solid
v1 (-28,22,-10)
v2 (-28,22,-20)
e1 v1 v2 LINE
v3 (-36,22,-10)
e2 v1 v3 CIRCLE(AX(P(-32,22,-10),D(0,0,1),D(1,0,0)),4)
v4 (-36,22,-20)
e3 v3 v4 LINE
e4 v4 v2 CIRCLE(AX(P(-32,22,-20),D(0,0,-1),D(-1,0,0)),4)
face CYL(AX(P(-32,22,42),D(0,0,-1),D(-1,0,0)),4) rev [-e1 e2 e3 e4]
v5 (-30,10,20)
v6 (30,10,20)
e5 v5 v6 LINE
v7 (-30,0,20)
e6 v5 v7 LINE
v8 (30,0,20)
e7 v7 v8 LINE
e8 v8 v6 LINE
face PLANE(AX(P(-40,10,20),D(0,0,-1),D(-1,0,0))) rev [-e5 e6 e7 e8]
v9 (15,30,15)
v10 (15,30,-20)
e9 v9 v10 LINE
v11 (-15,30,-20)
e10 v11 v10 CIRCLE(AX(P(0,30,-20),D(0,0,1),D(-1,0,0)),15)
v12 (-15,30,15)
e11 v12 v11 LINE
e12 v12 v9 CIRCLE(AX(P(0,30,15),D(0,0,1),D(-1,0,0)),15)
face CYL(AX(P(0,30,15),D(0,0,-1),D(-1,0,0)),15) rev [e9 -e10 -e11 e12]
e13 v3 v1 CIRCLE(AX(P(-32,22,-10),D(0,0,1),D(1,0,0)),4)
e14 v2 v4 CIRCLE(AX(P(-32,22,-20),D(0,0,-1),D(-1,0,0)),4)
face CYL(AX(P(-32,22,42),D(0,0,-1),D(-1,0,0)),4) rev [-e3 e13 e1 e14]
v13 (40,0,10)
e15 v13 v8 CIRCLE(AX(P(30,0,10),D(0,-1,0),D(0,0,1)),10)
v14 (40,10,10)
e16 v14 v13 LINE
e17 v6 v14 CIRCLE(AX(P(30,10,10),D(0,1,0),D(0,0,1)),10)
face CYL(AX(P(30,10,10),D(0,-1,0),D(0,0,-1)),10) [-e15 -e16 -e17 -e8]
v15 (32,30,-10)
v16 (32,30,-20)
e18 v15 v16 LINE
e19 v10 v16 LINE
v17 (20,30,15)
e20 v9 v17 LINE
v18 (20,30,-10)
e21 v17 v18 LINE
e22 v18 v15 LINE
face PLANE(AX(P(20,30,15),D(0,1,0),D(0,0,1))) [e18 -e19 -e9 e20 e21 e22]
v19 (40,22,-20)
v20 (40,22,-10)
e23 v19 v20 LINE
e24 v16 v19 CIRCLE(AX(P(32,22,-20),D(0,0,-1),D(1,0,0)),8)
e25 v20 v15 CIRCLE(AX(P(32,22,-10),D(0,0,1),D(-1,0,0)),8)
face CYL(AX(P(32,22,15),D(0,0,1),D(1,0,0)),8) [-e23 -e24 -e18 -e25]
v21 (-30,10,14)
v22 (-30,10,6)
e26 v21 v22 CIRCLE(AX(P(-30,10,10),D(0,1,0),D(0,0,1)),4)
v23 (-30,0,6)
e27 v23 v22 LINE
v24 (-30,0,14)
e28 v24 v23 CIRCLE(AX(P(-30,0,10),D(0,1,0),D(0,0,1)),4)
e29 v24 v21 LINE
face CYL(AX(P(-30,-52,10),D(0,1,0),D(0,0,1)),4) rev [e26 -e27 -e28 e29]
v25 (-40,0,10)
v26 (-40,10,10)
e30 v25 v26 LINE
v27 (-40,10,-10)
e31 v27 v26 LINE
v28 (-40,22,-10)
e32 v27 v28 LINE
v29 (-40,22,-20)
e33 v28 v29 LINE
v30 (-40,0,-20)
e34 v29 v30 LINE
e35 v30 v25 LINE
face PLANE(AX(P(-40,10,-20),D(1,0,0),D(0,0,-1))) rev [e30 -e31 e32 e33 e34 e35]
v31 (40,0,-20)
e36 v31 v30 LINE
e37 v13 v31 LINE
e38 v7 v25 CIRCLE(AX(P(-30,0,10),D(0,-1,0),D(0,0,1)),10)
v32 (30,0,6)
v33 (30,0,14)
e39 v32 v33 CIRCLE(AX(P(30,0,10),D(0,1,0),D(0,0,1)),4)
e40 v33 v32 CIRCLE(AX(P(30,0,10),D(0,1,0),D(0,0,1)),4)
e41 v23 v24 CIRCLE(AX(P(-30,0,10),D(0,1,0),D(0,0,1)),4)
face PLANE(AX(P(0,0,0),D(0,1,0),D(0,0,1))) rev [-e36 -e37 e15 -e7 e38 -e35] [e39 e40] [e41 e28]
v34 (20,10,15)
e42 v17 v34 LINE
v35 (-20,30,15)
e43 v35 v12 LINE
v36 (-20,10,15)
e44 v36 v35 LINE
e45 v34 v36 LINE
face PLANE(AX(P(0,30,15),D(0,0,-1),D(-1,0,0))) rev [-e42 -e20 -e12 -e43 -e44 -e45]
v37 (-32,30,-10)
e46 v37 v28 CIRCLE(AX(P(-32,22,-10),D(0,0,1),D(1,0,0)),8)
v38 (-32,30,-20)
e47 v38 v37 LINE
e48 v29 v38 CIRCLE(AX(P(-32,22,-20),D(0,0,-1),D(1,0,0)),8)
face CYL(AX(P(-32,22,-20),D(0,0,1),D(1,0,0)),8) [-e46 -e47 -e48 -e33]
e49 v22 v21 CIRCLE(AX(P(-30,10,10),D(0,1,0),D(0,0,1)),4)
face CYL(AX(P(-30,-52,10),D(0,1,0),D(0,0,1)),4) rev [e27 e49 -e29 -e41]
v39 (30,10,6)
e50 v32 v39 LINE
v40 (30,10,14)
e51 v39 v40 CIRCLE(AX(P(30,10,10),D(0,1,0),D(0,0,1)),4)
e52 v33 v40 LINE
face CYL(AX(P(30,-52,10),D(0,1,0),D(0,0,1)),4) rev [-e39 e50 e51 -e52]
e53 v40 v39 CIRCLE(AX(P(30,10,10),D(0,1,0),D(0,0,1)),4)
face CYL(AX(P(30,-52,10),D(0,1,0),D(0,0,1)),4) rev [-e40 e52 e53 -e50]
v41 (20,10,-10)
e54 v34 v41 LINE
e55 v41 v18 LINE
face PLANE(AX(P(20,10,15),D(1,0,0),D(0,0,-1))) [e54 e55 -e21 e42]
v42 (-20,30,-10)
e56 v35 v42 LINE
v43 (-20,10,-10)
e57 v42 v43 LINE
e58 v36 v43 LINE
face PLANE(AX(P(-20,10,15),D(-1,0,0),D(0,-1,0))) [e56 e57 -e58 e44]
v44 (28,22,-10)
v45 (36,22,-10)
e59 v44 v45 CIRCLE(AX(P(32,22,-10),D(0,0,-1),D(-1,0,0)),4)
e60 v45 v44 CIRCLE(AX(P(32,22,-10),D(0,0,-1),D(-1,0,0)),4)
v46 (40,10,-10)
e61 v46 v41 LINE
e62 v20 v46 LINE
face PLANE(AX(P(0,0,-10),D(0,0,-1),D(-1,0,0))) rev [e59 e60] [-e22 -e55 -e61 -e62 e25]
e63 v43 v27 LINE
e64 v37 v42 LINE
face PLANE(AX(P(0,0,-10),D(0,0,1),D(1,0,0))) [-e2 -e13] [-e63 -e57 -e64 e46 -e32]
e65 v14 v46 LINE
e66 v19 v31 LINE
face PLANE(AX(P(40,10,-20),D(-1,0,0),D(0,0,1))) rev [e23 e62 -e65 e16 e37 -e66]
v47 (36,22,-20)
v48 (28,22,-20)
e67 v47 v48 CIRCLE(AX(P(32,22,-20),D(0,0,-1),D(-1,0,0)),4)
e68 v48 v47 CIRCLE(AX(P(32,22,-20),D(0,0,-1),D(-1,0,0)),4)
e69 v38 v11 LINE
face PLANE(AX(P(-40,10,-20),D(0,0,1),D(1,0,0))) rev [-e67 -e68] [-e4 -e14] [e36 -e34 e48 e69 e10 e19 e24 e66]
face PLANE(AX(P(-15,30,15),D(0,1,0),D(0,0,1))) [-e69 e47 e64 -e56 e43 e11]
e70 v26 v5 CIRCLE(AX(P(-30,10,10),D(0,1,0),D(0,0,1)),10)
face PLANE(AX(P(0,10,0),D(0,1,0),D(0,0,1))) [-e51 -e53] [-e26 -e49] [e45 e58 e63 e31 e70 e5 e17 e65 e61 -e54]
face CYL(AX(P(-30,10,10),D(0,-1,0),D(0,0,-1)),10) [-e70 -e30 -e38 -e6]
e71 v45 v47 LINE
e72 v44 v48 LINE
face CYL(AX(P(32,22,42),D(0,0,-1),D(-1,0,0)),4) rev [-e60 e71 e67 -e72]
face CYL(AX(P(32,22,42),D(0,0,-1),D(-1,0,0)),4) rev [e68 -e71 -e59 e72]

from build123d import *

# Parameters (mm, degrees)
BASE_PLATE_SKETCH_W       = 80
BASE_PLATE_SKETCH_H       = 40
BASE_PLATE_80X40X10_DEPTH = 10
BASE_CORNER_FILLETS_R10_R = 10
SADDLE_BLOCK_DEPTH        = 35
LUG_PROFILE_SKETCH_W      = 20
LUG_PROFILE_SKETCH_H      = 20
UPRIGHT_LUGS_DEPTH        = 10
LUG_TOP_FILLETS_R8_R      = 8
LUG_HOLE_SKETCH_R         = 4
LUG_HOLES_8_DEPTH         = 62
BASE_HOLE_SKETCH_R        = 4
BASE_HOLES_8_DEPTH        = 62


with BuildPart() as part:
    # Base Plate Sketch → Base Plate 80x40x10 (new body)
    with BuildSketch(Plane(origin=(0, 0, 0), x_dir=(1, 0, 0), z_dir=(0, 1, 0))):
        Rectangle(BASE_PLATE_SKETCH_W, BASE_PLATE_SKETCH_H)
    extrude(amount=BASE_PLATE_80X40X10_DEPTH)

    # Base Corner Fillets R10
    base_corner_fillets_r10_edges = [part.edges().sort_by_distance(p)[0] for p in [
        (40, 5, 20),
        (-40, 5, 20),
    ]]
    fillet(base_corner_fillets_r10_edges, radius=BASE_CORNER_FILLETS_R10_R)

    # Saddle Block Sketch → Saddle Block (add)
    with BuildSketch(Plane(origin=(0, 0, -20), x_dir=(-1, 0, 0), z_dir=(0, 0, -1))):
        with BuildLine():
            Line((-20, 10), (20, 10))
            Line((20, 10), (20, 30))
            Line((20, 30), (15, 30))
            ThreePointArc((15, 30), (0, 15), (-15, 30))
            Line((-15, 30), (-20, 30))
            Line((-20, 30), (-20, 10))
        make_face()
    extrude(amount=-SADDLE_BLOCK_DEPTH)

    # Lug Profile Sketch → Upright Lugs (add)
    with BuildSketch(Plane(origin=(0, 0, -20), x_dir=(-1, 0, 0), z_dir=(0, 0, -1))):
        with Locations((-30, 20)):
            Rectangle(LUG_PROFILE_SKETCH_W, LUG_PROFILE_SKETCH_H)
        with Locations((30, 20)):
            Rectangle(LUG_PROFILE_SKETCH_W, LUG_PROFILE_SKETCH_H)
    extrude(amount=-UPRIGHT_LUGS_DEPTH)

    # Lug Top Fillets R8
    lug_top_fillets_r8_edges = [part.edges().sort_by_distance(p)[0] for p in [
        (40, 30, -15),
        (-40, 30, -15),
    ]]
    fillet(lug_top_fillets_r8_edges, radius=LUG_TOP_FILLETS_R8_R)

    # Lug Hole Sketch → Lug Holes Ø8 (cut)
    with BuildSketch(Plane(origin=(0, 0, -20), x_dir=(-1, 0, 0), z_dir=(0, 0, -1))):
        with Locations((32, 22)):
            Circle(LUG_HOLE_SKETCH_R)
        with Locations((-32, 22)):
            Circle(LUG_HOLE_SKETCH_R)
    extrude(amount=-LUG_HOLES_8_DEPTH, mode=Mode.SUBTRACT)

    # Base Hole Sketch → Base Holes Ø8 (cut)
    with BuildSketch(Plane(origin=(0, 10, 0), x_dir=(1, 0, 0), z_dir=(0, 1, 0))):
        with Locations(Location((-30, -10, 0), (0, 0, 270))):
            Circle(BASE_HOLE_SKETCH_R)
        with Locations(Location((30, -10, 0), (0, 0, 270))):
            Circle(BASE_HOLE_SKETCH_R)
    extrude(amount=-BASE_HOLES_8_DEPTH, mode=Mode.SUBTRACT)


solid = part.part
